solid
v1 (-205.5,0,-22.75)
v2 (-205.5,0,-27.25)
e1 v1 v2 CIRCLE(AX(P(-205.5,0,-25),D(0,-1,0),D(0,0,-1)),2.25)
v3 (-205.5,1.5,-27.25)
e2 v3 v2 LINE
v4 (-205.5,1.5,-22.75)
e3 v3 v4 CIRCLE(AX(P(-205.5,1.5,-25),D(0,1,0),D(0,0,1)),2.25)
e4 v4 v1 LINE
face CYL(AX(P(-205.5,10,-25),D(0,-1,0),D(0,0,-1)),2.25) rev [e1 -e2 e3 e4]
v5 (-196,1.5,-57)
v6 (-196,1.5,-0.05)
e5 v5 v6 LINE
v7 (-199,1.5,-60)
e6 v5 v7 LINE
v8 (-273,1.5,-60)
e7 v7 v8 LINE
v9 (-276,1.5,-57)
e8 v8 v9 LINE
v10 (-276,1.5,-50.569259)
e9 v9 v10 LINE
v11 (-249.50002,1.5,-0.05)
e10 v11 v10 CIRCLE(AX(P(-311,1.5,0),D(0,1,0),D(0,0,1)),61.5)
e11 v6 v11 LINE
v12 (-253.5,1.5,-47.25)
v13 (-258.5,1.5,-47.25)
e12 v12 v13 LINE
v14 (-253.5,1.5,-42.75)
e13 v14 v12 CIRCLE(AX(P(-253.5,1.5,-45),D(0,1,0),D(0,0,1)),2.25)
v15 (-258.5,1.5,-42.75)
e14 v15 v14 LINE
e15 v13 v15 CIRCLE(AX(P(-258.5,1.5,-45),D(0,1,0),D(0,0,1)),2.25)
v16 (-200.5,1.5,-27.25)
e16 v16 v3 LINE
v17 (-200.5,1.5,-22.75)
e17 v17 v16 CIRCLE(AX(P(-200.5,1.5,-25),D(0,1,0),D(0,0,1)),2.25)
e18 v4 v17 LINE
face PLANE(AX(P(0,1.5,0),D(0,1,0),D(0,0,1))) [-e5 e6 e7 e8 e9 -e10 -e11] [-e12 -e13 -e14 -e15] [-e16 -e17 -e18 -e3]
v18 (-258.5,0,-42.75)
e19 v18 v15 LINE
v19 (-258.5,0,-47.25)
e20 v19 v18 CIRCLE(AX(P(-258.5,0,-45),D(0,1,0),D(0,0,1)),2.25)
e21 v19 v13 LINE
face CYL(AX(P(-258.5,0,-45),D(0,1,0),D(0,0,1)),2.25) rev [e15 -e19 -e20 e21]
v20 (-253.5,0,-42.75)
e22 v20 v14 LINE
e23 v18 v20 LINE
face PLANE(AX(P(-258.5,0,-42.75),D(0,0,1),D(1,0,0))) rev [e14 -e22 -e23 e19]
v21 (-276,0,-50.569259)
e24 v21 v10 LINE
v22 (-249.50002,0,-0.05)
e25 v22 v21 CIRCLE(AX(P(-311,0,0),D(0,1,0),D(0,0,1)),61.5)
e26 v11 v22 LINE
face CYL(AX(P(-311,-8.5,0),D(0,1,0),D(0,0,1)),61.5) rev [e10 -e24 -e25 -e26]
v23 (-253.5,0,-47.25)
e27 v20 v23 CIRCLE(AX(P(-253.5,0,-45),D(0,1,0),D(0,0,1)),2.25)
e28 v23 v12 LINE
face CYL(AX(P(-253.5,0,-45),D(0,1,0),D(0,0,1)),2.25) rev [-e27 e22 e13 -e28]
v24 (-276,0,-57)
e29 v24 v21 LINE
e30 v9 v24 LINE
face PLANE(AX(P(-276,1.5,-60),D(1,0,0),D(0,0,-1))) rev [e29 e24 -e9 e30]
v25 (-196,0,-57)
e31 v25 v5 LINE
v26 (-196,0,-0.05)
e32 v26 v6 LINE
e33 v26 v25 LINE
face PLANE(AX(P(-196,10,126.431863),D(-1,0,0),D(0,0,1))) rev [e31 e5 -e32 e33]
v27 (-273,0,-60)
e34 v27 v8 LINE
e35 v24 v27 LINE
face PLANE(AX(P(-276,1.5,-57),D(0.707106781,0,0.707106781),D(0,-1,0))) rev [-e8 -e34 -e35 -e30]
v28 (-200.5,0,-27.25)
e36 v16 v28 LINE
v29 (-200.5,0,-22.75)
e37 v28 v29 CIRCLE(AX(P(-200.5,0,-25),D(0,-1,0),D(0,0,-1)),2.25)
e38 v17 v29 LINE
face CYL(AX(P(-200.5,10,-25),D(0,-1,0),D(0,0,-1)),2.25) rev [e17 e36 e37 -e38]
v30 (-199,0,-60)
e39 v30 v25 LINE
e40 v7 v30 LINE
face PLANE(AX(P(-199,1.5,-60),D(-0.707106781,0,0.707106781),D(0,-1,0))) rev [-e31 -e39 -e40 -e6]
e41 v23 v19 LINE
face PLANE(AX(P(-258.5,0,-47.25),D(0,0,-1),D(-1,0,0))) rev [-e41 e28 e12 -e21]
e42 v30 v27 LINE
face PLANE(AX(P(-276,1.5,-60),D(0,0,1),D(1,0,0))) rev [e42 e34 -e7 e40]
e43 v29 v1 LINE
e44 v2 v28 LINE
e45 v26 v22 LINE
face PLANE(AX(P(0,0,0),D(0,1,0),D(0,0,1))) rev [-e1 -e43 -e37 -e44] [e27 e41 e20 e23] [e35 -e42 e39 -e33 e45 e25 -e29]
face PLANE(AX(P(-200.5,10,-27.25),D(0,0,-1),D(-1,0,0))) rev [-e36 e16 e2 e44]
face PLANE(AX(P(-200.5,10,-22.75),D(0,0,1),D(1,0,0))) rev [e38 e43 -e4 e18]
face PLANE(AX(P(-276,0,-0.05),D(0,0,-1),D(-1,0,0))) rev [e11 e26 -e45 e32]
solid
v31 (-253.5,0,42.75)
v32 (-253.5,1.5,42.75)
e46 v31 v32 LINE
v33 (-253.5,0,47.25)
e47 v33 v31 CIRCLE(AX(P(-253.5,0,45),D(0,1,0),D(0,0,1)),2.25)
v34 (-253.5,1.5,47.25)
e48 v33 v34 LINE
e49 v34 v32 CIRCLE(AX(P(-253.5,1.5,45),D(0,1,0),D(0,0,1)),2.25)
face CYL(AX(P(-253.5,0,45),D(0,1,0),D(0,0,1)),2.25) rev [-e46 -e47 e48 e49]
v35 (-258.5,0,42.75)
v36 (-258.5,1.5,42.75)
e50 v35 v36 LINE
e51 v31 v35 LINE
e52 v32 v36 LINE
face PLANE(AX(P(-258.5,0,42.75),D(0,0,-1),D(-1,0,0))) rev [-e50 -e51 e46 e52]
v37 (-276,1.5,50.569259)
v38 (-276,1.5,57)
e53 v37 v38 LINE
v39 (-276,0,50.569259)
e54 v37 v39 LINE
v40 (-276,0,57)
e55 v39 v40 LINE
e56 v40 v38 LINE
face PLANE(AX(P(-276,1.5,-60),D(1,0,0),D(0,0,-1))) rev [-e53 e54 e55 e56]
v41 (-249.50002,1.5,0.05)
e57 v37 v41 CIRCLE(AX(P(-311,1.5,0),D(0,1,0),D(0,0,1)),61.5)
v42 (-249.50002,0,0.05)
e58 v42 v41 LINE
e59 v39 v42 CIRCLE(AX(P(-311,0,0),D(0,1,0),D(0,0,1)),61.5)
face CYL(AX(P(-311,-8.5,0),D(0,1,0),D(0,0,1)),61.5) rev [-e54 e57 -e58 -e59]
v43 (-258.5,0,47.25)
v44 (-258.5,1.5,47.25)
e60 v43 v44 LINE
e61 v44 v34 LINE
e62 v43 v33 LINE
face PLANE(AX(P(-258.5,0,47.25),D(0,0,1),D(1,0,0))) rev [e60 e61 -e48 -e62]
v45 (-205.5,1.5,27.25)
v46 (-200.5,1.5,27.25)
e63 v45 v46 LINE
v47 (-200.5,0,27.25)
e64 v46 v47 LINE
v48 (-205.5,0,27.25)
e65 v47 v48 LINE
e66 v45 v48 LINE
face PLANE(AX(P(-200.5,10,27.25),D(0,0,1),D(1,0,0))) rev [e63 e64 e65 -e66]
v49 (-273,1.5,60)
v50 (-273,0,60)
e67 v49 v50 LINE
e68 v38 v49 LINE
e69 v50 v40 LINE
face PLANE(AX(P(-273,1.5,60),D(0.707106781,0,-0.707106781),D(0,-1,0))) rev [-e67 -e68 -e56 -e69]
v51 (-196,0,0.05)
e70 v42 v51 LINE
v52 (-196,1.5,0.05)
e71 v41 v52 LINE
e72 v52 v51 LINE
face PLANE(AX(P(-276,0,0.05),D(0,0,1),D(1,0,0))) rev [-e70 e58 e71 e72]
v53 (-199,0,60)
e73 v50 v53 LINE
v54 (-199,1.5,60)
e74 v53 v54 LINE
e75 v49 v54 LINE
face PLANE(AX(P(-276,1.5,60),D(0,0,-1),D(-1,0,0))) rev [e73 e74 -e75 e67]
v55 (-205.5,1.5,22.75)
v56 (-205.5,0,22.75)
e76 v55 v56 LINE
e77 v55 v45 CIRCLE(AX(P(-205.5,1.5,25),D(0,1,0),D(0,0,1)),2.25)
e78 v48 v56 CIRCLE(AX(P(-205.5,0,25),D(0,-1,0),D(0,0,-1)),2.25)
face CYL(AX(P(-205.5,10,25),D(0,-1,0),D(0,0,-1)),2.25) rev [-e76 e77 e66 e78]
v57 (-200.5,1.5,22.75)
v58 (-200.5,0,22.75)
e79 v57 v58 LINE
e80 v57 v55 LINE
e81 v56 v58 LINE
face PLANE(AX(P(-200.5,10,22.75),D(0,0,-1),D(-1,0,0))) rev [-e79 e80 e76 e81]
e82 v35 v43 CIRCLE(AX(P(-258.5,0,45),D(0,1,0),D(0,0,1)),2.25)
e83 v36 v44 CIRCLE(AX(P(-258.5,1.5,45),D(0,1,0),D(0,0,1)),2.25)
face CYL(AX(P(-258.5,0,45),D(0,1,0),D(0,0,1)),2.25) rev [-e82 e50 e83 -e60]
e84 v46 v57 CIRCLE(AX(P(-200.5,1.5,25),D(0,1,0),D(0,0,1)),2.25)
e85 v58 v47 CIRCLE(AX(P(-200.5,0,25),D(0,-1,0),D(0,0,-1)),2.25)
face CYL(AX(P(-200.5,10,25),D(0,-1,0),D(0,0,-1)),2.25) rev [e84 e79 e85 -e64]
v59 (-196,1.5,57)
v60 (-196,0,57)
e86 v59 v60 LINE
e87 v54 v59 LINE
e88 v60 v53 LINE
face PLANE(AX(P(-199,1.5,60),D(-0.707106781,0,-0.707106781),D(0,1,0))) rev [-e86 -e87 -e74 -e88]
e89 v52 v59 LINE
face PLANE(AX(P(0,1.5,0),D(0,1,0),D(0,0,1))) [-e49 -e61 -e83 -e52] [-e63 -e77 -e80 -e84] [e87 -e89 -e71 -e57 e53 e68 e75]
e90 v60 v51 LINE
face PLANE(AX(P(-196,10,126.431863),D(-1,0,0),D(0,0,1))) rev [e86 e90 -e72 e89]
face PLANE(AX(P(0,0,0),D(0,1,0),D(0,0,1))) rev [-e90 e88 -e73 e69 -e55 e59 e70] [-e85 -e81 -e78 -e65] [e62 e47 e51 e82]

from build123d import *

# Parameters (mm, degrees)
SKETCH1_W           = 552
SKETCH1_H           = 120
BOSS_EXTRUDE1_DEPTH = 1.5
CHAMFER1_SIZE       = 3
CHAMFER2_SIZE       = 3
CUT_EXTRUDE6_DEPTH  = 283.45043813
SKETCH13_W          = 552
SKETCH13_H          = 0.1
CUT_EXTRUDE7_DEPTH  = 283.45043813
CUT_EXTRUDE9_DEPTH  = 283.45043813
SKETCH16_R          = 61.5
CUT_EXTRUDE10_DEPTH = 10
SKETCH18_W          = 998.789859015
SKETCH18_H          = 252.863725976
CUT_EXTRUDE11_DEPTH = 10
CUT_EXTRUDE12_DEPTH = 10
CHAMFER3_SIZE       = 3
CHAMFER4_SIZE       = 3


with BuildPart() as part:
    # Sketch1 → Boss-Extrude1 (new body)
    with BuildSketch(Plane(origin=(0, 0, 0), x_dir=(1, 0, 0), z_dir=(0, 1, 0))):
        Rectangle(SKETCH1_W, SKETCH1_H)
    extrude(amount=BOSS_EXTRUDE1_DEPTH)

    # Chamfer1
    chamfer1_edges = [part.edges().sort_by_distance(p)[0] for p in [
        (276, 0.75, 60),
        (276, 0.75, -60),
    ]]
    chamfer(chamfer1_edges, length=CHAMFER1_SIZE)

    # Chamfer2
    chamfer2_edges = [part.edges().sort_by_distance(p)[0] for p in [
        (-276, 0.75, 60),
        (-276, 0.75, -60),
    ]]
    chamfer(chamfer2_edges, length=CHAMFER2_SIZE)

    # Sketch12 → Cut-Extrude6 (cut, through all)
    with BuildSketch(Plane(origin=(0, 1.5, 0), x_dir=(1, 0, 0), z_dir=(0, 1, 0))):
        with BuildLine():
            Line((-258.5, 47.25), (-253.5, 47.25))
            ThreePointArc((-253.5, 47.25), (-251.25, 45), (-253.5, 42.75))
            Line((-253.5, 42.75), (-258.5, 42.75))
            ThreePointArc((-258.5, 42.75), (-260.75, 45), (-258.5, 47.25))
        make_face()
        with BuildLine():
            Line((-258.5, -42.75), (-253.5, -42.75))
            ThreePointArc((-253.5, -42.75), (-251.25, -45), (-253.5, -47.25))
            Line((-253.5, -47.25), (-258.5, -47.25))
            ThreePointArc((-258.5, -47.25), (-260.75, -45), (-258.5, -42.75))
        make_face()
    extrude(amount=-CUT_EXTRUDE6_DEPTH, mode=Mode.SUBTRACT)

    # Sketch13 → Cut-Extrude7 (cut, through all)
    with BuildSketch(Plane(origin=(0, 1.5, 0), x_dir=(1, 0, 0), z_dir=(0, 1, 0))):
        Rectangle(SKETCH13_W, SKETCH13_H)
    extrude(amount=-CUT_EXTRUDE7_DEPTH, mode=Mode.SUBTRACT)


with BuildPart() as cut_extrude7_piece_1:
    # of the separate pieces the step leaves, piece 1, a body of its own (cut_extrude7_pieces)
    add(part.part.solids().sort_by_distance((-273, 0, -60))[0])


with BuildPart() as cut_extrude7_piece_2:
    # of the separate pieces the step leaves, piece 2, a body of its own (cut_extrude7_pieces)
    add(part.part.solids().sort_by_distance((-276, 0, 57))[0])


with BuildPart() as cut_extrude9_tool:
    # Sketch15 → Cut-Extrude9 (new, through all)
    with BuildSketch(Plane(origin=(0, 1.5, 0), x_dir=(1, 0, 0), z_dir=(0, 1, 0))):
        with BuildLine():
            Line((52, 35.95), (-14, 35.95))
            ThreePointArc((-14, 35.95), (-16.121320344, 35.071320344), (-17, 32.95))
            Line((-17, 32.95), (-17, -33.05))
            ThreePointArc((-17, -33.05), (-16.121320344, -35.171320344), (-14, -36.05))
            Line((-14, -36.05), (52, -36.05))
            ThreePointArc((52, -36.05), (54.121320344, -35.171320344), (55, -33.05))
            Line((55, -33.05), (55, 32.95))
            ThreePointArc((55, 32.95), (54.121320344, 35.071320344), (52, 35.95))
        make_face()
    extrude(amount=-CUT_EXTRUDE9_DEPTH)


with BuildPart() as cut_extrude7_piece_1_1:
    add(cut_extrude7_piece_1.part)

    # Cut-Extrude9: cut by cut_extrude9_tool
    add(cut_extrude9_tool.part, mode=Mode.SUBTRACT)


with BuildPart() as cut_extrude7_piece_2_1:
    add(cut_extrude7_piece_2.part)

    # Cut-Extrude9: cut by cut_extrude9_tool
    add(cut_extrude9_tool.part, mode=Mode.SUBTRACT)


with BuildPart() as cut_extrude10_tool:
    # Sketch16 → Cut-Extrude10 (new body)
    with BuildSketch(Plane(origin=(0, 1.5, 0), x_dir=(1, 0, 0), z_dir=(0, 1, 0))):
        with Locations((311, 0)):
            Circle(SKETCH16_R)
        with Locations((-311, 0)):
            Circle(SKETCH16_R)
    extrude(amount=-CUT_EXTRUDE10_DEPTH)


with BuildPart() as cut_extrude7_piece_1_2:
    add(cut_extrude7_piece_1_1.part)

    # Cut-Extrude10: cut by cut_extrude10_tool
    add(cut_extrude10_tool.part, mode=Mode.SUBTRACT)


with BuildPart() as cut_extrude7_piece_2_2:
    add(cut_extrude7_piece_2_1.part)

    # Cut-Extrude10: cut by cut_extrude10_tool
    add(cut_extrude10_tool.part, mode=Mode.SUBTRACT)


with BuildPart() as cut_extrude11_tool:
    # Sketch18 → Cut-Extrude11 (new body)
    with BuildSketch(Plane.XZ):
        with Locations((303.394929508, 0)):
            Rectangle(SKETCH18_W, SKETCH18_H)
    extrude(amount=-CUT_EXTRUDE11_DEPTH)


with BuildPart() as cut_extrude7_piece_1_3:
    add(cut_extrude7_piece_1_2.part)

    # Cut-Extrude11: cut by cut_extrude11_tool
    add(cut_extrude11_tool.part, mode=Mode.SUBTRACT)


with BuildPart() as cut_extrude7_piece_2_3:
    add(cut_extrude7_piece_2_2.part)

    # Cut-Extrude11: cut by cut_extrude11_tool
    add(cut_extrude11_tool.part, mode=Mode.SUBTRACT)


with BuildPart() as cut_extrude12_tool:
    # Sketch17 → Cut-Extrude12 (new body)
    with BuildSketch(Plane.XZ):
        with BuildLine():
            Line((-200.5, -27.25), (-205.5, -27.25))
            ThreePointArc((-205.5, -27.25), (-207.75, -25), (-205.5, -22.75))
            Line((-205.5, -22.75), (-200.5, -22.75))
            ThreePointArc((-200.5, -22.75), (-198.25, -25), (-200.5, -27.25))
        make_face()
        with BuildLine():
            Line((-200.5, 22.75), (-205.5, 22.75))
            ThreePointArc((-205.5, 22.75), (-207.75, 25), (-205.5, 27.25))
            Line((-205.5, 27.25), (-200.5, 27.25))
            ThreePointArc((-200.5, 27.25), (-198.25, 25), (-200.5, 22.75))
        make_face()
    extrude(amount=-CUT_EXTRUDE12_DEPTH)


with BuildPart() as cut_extrude7_piece_1_4:
    add(cut_extrude7_piece_1_3.part)

    # Cut-Extrude12: cut by cut_extrude12_tool
    add(cut_extrude12_tool.part, mode=Mode.SUBTRACT)

    # Chamfer4
    chamfer4_edges = [cut_extrude7_piece_1_4.edges().sort_by_distance(p)[0] for p in [
        (-196, 0.75, -60),
    ]]
    chamfer(chamfer4_edges, length=CHAMFER4_SIZE)


with BuildPart() as cut_extrude7_piece_2_4:
    add(cut_extrude7_piece_2_3.part)

    # Cut-Extrude12: cut by cut_extrude12_tool
    add(cut_extrude12_tool.part, mode=Mode.SUBTRACT)

    # Chamfer3
    chamfer3_edges = [cut_extrude7_piece_2_4.edges().sort_by_distance(p)[0] for p in [
        (-196, 0.75, 60),
    ]]
    chamfer(chamfer3_edges, length=CHAMFER3_SIZE)


solid = Compound([cut_extrude7_piece_1_4.part, cut_extrude7_piece_2_4.part])
